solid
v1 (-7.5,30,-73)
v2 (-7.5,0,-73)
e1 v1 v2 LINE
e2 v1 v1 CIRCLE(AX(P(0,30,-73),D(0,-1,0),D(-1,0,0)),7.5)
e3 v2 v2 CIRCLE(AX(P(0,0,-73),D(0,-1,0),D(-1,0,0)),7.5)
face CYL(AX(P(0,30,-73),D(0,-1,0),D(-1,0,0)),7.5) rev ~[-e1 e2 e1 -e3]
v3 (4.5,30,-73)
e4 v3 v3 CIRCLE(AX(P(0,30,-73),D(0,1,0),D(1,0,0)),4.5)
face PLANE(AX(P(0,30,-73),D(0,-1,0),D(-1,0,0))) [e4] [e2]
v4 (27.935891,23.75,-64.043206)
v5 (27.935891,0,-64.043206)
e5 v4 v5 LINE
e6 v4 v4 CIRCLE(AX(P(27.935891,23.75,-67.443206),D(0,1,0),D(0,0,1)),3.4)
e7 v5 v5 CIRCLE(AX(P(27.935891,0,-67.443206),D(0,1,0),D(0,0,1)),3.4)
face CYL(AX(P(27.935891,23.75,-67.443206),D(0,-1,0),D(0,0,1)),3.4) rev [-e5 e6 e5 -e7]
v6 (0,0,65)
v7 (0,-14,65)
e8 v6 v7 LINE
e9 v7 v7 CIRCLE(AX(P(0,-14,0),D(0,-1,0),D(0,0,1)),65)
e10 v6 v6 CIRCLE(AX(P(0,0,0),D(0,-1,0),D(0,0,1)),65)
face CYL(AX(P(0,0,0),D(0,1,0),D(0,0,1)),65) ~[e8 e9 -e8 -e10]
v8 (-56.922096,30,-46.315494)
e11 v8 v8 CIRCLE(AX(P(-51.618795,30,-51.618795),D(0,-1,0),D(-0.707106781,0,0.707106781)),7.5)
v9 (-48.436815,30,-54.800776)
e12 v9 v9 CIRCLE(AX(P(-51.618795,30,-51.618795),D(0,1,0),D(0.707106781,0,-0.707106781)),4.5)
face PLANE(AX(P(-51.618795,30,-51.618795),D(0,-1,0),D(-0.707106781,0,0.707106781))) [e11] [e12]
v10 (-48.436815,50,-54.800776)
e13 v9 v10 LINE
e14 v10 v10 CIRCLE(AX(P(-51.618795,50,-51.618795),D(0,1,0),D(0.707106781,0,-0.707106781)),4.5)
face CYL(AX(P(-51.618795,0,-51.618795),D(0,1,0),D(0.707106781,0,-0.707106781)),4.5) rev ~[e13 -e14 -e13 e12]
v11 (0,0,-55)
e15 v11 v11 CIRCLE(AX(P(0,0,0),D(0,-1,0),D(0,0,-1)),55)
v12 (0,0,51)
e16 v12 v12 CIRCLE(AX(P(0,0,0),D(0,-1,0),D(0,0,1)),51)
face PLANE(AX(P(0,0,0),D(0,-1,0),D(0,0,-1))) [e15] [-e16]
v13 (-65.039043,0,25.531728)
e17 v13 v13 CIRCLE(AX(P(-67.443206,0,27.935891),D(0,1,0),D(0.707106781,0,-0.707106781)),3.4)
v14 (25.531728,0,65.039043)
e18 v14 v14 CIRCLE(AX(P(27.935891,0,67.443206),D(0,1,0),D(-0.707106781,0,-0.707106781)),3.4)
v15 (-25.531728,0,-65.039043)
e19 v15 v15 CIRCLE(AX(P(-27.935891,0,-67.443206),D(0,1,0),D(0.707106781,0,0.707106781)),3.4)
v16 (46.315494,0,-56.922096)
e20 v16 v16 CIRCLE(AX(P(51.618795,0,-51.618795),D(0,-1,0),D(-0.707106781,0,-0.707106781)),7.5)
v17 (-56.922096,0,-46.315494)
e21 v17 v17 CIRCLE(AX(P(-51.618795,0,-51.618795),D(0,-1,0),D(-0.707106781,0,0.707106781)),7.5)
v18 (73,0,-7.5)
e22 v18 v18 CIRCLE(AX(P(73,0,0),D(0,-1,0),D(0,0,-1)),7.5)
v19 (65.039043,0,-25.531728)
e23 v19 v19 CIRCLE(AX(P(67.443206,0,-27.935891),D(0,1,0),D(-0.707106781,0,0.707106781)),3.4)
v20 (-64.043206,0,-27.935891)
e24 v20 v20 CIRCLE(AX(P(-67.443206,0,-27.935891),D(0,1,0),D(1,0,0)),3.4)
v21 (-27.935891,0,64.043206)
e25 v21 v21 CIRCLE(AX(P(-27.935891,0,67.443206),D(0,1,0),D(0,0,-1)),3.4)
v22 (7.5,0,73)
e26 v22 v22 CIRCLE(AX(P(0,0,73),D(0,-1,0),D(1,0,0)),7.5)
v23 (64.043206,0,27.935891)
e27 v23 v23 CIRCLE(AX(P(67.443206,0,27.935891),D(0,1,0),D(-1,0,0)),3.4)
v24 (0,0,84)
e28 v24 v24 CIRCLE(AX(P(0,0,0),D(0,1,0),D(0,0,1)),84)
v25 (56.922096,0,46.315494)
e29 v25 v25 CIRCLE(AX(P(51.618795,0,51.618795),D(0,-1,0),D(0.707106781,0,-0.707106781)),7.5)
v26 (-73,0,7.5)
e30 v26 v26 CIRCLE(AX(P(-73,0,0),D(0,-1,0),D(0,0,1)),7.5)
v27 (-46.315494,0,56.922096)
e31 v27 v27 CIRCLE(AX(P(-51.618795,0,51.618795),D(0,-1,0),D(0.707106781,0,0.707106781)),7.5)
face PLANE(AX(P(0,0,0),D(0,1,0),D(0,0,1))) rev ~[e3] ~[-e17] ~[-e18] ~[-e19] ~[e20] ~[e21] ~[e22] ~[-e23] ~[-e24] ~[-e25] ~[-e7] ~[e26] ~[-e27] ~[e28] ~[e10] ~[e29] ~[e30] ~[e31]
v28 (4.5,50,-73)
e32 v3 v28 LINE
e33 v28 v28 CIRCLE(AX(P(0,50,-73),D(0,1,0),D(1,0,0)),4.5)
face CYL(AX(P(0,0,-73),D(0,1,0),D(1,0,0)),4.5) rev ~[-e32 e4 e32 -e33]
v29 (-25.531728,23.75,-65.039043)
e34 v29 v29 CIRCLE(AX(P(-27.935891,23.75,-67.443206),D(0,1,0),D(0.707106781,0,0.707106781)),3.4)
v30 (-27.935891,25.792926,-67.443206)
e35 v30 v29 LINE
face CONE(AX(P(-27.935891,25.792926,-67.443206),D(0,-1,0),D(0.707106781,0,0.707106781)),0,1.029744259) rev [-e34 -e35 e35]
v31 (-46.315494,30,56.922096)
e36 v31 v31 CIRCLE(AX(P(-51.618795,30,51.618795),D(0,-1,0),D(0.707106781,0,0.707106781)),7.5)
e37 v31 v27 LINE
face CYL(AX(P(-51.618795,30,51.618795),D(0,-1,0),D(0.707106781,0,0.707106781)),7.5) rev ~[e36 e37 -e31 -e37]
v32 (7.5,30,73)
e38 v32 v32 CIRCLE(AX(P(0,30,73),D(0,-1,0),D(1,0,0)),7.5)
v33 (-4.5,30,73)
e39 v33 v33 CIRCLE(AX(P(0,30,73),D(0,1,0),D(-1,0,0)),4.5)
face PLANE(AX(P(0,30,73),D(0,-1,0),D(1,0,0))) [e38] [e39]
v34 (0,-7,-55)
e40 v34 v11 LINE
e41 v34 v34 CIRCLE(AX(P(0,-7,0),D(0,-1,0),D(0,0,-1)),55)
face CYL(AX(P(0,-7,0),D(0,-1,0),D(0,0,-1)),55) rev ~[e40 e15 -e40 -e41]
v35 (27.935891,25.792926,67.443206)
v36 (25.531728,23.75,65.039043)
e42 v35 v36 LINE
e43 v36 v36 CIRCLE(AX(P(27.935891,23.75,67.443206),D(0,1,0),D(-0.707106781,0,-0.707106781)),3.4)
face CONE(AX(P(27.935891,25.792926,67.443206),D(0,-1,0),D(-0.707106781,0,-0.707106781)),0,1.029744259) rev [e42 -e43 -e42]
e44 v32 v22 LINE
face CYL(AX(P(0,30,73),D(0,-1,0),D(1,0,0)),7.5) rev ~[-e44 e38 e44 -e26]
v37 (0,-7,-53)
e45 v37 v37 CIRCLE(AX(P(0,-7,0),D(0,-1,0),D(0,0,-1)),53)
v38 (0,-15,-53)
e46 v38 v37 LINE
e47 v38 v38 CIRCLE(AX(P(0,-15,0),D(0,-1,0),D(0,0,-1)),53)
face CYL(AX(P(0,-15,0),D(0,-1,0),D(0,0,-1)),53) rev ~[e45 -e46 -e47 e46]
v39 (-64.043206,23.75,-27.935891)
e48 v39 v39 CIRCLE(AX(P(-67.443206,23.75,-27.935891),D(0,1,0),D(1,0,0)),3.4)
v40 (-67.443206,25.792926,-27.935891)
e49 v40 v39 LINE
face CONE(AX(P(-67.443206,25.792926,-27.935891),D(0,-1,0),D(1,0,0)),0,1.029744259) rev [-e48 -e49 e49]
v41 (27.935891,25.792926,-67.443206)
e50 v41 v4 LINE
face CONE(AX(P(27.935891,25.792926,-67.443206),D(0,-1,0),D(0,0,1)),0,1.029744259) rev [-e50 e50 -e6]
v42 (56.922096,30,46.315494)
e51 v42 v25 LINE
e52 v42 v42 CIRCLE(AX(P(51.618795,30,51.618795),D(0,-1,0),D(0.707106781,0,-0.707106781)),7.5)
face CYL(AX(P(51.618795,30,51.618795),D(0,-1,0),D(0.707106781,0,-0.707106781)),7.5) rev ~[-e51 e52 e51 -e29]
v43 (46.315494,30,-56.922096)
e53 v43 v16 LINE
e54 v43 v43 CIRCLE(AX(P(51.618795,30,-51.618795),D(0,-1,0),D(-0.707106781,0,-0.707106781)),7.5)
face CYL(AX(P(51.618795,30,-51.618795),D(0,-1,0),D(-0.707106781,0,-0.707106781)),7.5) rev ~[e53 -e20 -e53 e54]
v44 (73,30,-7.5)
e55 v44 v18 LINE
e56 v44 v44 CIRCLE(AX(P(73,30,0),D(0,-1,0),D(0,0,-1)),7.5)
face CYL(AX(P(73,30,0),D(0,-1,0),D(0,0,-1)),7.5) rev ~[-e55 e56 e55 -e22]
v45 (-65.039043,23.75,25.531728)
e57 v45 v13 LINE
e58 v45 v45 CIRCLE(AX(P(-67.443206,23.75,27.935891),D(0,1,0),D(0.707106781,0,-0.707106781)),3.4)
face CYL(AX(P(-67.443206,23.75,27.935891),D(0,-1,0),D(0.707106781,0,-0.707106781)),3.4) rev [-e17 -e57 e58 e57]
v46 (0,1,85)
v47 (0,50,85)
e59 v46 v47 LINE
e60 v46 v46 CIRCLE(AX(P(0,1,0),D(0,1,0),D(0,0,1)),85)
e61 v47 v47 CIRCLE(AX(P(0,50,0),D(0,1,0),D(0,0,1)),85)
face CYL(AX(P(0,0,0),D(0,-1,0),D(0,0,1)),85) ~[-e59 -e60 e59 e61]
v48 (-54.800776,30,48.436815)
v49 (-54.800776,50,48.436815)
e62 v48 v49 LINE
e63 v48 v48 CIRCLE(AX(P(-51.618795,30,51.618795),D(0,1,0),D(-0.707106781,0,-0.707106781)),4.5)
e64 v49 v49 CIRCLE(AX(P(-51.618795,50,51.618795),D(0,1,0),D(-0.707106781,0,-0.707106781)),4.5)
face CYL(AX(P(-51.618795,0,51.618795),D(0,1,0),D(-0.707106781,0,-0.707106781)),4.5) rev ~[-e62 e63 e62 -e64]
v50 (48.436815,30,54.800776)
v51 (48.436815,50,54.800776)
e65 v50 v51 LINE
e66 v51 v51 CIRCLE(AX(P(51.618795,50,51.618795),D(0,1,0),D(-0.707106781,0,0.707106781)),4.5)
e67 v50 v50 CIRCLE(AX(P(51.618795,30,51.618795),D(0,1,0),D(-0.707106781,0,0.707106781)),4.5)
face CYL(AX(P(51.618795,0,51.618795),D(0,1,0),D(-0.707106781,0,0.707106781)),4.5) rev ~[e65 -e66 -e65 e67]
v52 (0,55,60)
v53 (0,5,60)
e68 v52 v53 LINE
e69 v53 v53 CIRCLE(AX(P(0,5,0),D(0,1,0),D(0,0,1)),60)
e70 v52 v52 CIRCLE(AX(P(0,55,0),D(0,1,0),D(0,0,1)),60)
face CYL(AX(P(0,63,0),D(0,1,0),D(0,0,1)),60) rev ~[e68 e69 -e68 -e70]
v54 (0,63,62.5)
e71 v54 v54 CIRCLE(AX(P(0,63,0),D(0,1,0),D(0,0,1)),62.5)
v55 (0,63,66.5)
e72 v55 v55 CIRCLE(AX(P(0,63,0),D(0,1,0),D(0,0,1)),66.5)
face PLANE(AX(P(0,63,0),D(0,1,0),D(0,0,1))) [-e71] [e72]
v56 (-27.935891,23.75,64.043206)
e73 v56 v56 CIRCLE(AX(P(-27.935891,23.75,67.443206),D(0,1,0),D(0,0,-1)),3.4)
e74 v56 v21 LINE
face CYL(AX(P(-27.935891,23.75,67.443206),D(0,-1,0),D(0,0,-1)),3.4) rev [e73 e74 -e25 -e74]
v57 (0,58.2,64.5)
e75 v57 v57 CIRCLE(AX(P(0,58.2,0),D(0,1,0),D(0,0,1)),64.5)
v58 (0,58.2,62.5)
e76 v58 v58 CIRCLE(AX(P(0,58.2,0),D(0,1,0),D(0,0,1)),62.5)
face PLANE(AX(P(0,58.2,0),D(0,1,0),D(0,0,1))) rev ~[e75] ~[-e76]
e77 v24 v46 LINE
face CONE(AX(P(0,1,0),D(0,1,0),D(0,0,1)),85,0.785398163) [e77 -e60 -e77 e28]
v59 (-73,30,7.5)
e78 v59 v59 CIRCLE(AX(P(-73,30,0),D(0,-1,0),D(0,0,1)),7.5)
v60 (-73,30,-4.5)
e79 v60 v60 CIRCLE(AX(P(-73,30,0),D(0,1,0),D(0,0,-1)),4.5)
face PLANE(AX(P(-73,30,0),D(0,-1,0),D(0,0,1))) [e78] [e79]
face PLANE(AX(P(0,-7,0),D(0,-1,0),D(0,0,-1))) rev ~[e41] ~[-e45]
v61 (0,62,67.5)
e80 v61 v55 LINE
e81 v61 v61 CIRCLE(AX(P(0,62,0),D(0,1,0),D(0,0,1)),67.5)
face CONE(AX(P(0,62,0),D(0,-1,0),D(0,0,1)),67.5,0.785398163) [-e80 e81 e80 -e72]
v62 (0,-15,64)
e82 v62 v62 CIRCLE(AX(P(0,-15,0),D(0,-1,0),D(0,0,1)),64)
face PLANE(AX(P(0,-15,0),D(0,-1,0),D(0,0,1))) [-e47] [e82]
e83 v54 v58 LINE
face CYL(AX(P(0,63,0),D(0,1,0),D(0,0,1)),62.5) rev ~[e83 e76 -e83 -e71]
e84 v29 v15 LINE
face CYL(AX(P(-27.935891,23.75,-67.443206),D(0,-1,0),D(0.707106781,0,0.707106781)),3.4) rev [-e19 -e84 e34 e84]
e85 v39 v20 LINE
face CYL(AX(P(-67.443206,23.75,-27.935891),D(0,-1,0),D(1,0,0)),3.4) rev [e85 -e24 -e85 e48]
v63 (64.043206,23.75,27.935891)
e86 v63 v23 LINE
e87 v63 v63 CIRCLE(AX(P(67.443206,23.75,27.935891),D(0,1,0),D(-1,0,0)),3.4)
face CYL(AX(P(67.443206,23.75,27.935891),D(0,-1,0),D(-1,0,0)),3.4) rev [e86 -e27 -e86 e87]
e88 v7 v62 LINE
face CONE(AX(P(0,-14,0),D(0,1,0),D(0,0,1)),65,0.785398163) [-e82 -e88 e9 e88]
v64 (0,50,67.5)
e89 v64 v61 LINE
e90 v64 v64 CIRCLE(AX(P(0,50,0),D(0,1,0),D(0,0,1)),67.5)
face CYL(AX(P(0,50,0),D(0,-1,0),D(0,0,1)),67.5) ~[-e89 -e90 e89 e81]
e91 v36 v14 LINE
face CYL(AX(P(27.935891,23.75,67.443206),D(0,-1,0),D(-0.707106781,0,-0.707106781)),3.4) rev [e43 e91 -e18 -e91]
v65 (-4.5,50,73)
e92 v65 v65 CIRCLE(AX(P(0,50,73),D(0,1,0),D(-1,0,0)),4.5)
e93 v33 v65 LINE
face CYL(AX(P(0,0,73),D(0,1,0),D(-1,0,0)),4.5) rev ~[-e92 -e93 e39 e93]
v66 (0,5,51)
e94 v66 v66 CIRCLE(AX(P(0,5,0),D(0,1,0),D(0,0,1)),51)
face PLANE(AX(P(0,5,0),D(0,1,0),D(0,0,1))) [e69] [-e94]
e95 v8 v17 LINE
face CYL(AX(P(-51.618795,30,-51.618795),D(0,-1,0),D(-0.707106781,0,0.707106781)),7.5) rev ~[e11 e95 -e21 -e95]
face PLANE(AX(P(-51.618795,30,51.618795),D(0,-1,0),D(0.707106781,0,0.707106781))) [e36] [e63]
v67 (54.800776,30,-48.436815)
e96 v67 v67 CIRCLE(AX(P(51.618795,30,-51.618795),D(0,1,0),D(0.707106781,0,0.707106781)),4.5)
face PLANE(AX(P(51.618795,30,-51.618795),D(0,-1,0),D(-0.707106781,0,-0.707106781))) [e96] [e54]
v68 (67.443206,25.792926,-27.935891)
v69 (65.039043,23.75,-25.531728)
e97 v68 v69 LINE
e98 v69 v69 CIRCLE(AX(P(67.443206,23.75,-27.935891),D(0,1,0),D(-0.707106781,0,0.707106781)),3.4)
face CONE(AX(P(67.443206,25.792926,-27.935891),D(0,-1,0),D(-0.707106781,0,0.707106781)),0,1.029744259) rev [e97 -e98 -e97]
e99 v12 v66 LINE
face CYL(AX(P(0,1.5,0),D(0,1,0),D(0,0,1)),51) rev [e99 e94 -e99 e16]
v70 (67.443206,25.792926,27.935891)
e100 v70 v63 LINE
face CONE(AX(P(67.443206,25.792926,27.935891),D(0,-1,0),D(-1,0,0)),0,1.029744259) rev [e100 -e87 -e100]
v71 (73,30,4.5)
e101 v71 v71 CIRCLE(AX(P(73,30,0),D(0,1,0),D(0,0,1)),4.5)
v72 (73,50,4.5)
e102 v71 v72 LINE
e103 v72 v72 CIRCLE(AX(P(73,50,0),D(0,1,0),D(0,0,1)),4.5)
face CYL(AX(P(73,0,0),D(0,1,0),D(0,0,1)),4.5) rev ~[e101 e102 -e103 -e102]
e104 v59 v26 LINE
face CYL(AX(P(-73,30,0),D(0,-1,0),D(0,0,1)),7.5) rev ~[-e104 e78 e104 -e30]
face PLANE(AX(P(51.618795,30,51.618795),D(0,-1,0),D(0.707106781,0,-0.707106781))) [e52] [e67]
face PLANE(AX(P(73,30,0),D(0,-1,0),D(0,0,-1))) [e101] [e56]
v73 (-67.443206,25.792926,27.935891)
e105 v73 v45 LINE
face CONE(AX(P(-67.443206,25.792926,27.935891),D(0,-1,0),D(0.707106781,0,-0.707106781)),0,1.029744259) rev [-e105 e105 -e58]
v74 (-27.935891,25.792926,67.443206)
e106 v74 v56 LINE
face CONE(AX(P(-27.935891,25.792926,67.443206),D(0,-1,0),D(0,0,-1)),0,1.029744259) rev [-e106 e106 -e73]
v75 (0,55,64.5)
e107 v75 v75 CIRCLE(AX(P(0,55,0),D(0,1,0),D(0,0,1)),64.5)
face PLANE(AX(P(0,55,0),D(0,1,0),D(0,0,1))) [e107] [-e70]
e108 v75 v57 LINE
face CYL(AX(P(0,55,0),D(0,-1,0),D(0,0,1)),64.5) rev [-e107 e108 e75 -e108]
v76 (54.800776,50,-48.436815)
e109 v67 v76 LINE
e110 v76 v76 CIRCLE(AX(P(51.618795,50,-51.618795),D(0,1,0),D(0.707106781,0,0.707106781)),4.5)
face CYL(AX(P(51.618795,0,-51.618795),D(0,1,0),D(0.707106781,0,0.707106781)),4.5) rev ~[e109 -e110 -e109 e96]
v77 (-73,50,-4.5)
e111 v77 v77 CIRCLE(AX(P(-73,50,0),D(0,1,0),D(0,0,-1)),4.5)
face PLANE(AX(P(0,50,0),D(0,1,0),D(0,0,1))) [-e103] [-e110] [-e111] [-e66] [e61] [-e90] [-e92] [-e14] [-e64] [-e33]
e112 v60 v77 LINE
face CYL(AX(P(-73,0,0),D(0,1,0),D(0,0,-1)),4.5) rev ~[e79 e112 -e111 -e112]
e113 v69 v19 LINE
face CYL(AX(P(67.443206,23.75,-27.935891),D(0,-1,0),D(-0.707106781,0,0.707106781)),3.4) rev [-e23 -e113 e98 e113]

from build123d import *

# Parameters (mm, degrees)
SKETCH1_R                                          = 85
BOSS_EXTRUDE1_DEPTH                                = 50
SKETCH2_R                                          = 67.5
BOSS_EXTRUDE2_DEPTH                                = 13
SKETCH3_R                                          = 65
BOSS_EXTRUDE3_DEPTH                                = 15
CHAMFER1_SIZE                                      = 1
SKETCH4_R                                          = 52.5
CUT_EXTRUDE1_DEPTH                                 = 55
SKETCH5_R                                          = 51
CUT_EXTRUDE2_DEPTH                                 = 133.193040664
CUT_EXTRUDE3_START                                 = -8
SKETCH6_R                                          = 55
CUT_EXTRUDE3_DEPTH                                 = 8.5
HOLE_SIZE_BASED_ON_SOCKET_HEAD_CAP_SCR_D           = 9
HOLE_SIZE_BASED_ON_SOCKET_HEAD_CAP_SCR_CBORE_D     = 15
HOLE_SIZE_BASED_ON_SOCKET_HEAD_CAP_SCR_CBORE_DEPTH = 30
CIRPATTERN1_COUNT                                  = 8
CHAMFER2_SIZE                                      = 1
SKETCH15_R                                         = 55
SKETCH15_R_2                                       = 51
BOSS_EXTRUDE4_DEPTH                                = 1.5
CIRPATTERN3_COUNT                                  = 8
SKETCH20_R                                         = 53
CUT_EXTRUDE8_DEPTH                                 = 8
SKETCH22_R                                         = 60
CUT_EXTRUDE11_DEPTH                                = 58
CUT_EXTRUDE12_START                                = -8
SKETCH23_R                                         = 64.5
CUT_EXTRUDE12_DEPTH                                = 3.2
SKETCH25_R                                         = 62.5
CUT_EXTRUDE13_DEPTH                                = 8


with BuildPart() as part:
    # Sketch1 → Boss-Extrude1 (new body)
    with BuildSketch(Plane(origin=(0, 0, 0), x_dir=(1, 0, 0), z_dir=(0, 1, 0))):
        with Locations(Location((0, 0, 0), (0, 0, 270))):
            Circle(SKETCH1_R)
    extrude(amount=BOSS_EXTRUDE1_DEPTH)

    # Sketch2 → Boss-Extrude2 (add)
    with BuildSketch(Plane(origin=(0, 50, 0), x_dir=(1, 0, 0), z_dir=(0, 1, 0))):
        with Locations(Location((0, 0, 0), (0, 0, 270))):
            Circle(SKETCH2_R)
    extrude(amount=BOSS_EXTRUDE2_DEPTH)

    # Sketch3 → Boss-Extrude3 (add)
    with BuildSketch(Plane.XZ):
        with Locations(Location((0, 0, 0), (0, 0, 90))):
            Circle(SKETCH3_R)
    extrude(amount=BOSS_EXTRUDE3_DEPTH)

    # Chamfer1
    chamfer1_edges = [part.edges().sort_by_distance(p)[0] for p in [
        (0, -15, -65),
        (0, 63, -67.5),
    ]]
    chamfer(chamfer1_edges, length=CHAMFER1_SIZE)

    # Sketch4 → Cut-Extrude1 (cut)
    with BuildSketch(Plane(origin=(0, 63, 0), x_dir=(1, 0, 0), z_dir=(0, 1, 0))):
        with Locations(Location((0, 0, 0), (0, 0, 270))):
            Circle(SKETCH4_R)
    extrude(amount=-CUT_EXTRUDE1_DEPTH, mode=Mode.SUBTRACT)

    # Sketch5 → Cut-Extrude2 (cut, through all)
    with BuildSketch(Plane(origin=(0, 8, 0), x_dir=(1, 0, 0), z_dir=(0, 1, 0))):
        with Locations(Location((0, 0, 0), (0, 0, 270))):
            Circle(SKETCH5_R)
    extrude(amount=-CUT_EXTRUDE2_DEPTH, mode=Mode.SUBTRACT)

    # Sketch6 → Cut-Extrude3 (cut)
    with BuildSketch(Plane.XZ.offset(15).offset(CUT_EXTRUDE3_START)):
        with Locations(Location((0, 0, 0), (0, 0, 270))):
            Circle(SKETCH6_R)
    extrude(amount=-CUT_EXTRUDE3_DEPTH, mode=Mode.SUBTRACT)

    # Hole size (% based on socket head cap screw type)1 (through all)
    with Locations(Plane(origin=(0, 0, 0), x_dir=(-1, 0, 0), z_dir=(0, -1, 0))):
        with Locations((0, 73)):
            hole_size_based_on_socket_head_cap_scr = CounterBoreHole(HOLE_SIZE_BASED_ON_SOCKET_HEAD_CAP_SCR_D / 2, HOLE_SIZE_BASED_ON_SOCKET_HEAD_CAP_SCR_CBORE_D / 2, HOLE_SIZE_BASED_ON_SOCKET_HEAD_CAP_SCR_CBORE_DEPTH)

    # CirPattern1: Hole size (% based on socket head cap screw type)1 ×8 about axis
    cirpattern1_axis = Axis((0, 0, 0), (0, 1, 0))
    for i in range(1, CIRPATTERN1_COUNT):
        add(hole_size_based_on_socket_head_cap_scr.rotate(cirpattern1_axis, i * 360 / CIRPATTERN1_COUNT), mode=Mode.SUBTRACT)

    # Chamfer2
    chamfer2_edges = [part.edges().sort_by_distance(p)[0] for p in [
        (0, 0, -85),
    ]]
    chamfer(chamfer2_edges, length=CHAMFER2_SIZE)

    # Sketch15 → Boss-Extrude4 (add)
    with BuildSketch(Plane.XZ.offset(-1.5)):
        with Locations(Location((0, 0, 0), (0, 0, 270))):
            Circle(SKETCH15_R)
        with Locations(Location((0, 0, 0), (0, 0, 90))):
            Circle(SKETCH15_R_2, mode=Mode.SUBTRACT)
    extrude(amount=BOSS_EXTRUDE4_DEPTH)

    # Sketch19 → M8 Tapped Hole1 (revolve, cut)
    with BuildSketch(Plane(origin=(-27.935890563, 0, 67.443205873), x_dir=(0, 0, -1), z_dir=(1, 0, 0))):
        Polygon((0, 0), (0, 25.792926105), (3.4, 23.75), (3.4, 0), align=None)
    m8_tapped_hole1 = revolve(axis=Axis((-27.935890563, -6.35, 67.443205873), (0, 1, 0)), mode=Mode.SUBTRACT)

    # CirPattern3: M8 Tapped Hole1 ×8 about axis
    cirpattern3_axis = Axis((0, 0, 0), (0, 1, 0))
    for i in range(1, CIRPATTERN3_COUNT):
        add(m8_tapped_hole1.rotate(cirpattern3_axis, i * 360 / CIRPATTERN3_COUNT), mode=Mode.SUBTRACT)

    # Sketch20 → Cut-Extrude8 (cut)
    with BuildSketch(Plane.XZ.offset(15)):
        with Locations(Location((0, 0, 0), (0, 0, 270))):
            Circle(SKETCH20_R)
    extrude(amount=-CUT_EXTRUDE8_DEPTH, mode=Mode.SUBTRACT)

    # Sketch22 → Cut-Extrude11 (cut)
    with BuildSketch(Plane(origin=(0, 63, 0), x_dir=(1, 0, 0), z_dir=(0, 1, 0))):
        with Locations(Location((0, 0, 0), (0, 0, 270))):
            Circle(SKETCH22_R)
    extrude(amount=-CUT_EXTRUDE11_DEPTH, mode=Mode.SUBTRACT)

    # Sketch23 → Cut-Extrude12 (cut)
    with BuildSketch(Plane(origin=(0, 63, 0), x_dir=(1, 0, 0), z_dir=(0, 1, 0)).offset(CUT_EXTRUDE12_START)):
        with Locations(Location((0, 0, 0), (0, 0, 270))):
            Circle(SKETCH23_R)
    extrude(amount=CUT_EXTRUDE12_DEPTH, mode=Mode.SUBTRACT)

    # Sketch25 → Cut-Extrude13 (cut)
    with BuildSketch(Plane(origin=(0, 63, 0), x_dir=(1, 0, 0), z_dir=(0, 1, 0))):
        with Locations(Location((0, 0, 0), (0, 0, 270))):
            Circle(SKETCH25_R)
    extrude(amount=-CUT_EXTRUDE13_DEPTH, mode=Mode.SUBTRACT)


solid = part.part
